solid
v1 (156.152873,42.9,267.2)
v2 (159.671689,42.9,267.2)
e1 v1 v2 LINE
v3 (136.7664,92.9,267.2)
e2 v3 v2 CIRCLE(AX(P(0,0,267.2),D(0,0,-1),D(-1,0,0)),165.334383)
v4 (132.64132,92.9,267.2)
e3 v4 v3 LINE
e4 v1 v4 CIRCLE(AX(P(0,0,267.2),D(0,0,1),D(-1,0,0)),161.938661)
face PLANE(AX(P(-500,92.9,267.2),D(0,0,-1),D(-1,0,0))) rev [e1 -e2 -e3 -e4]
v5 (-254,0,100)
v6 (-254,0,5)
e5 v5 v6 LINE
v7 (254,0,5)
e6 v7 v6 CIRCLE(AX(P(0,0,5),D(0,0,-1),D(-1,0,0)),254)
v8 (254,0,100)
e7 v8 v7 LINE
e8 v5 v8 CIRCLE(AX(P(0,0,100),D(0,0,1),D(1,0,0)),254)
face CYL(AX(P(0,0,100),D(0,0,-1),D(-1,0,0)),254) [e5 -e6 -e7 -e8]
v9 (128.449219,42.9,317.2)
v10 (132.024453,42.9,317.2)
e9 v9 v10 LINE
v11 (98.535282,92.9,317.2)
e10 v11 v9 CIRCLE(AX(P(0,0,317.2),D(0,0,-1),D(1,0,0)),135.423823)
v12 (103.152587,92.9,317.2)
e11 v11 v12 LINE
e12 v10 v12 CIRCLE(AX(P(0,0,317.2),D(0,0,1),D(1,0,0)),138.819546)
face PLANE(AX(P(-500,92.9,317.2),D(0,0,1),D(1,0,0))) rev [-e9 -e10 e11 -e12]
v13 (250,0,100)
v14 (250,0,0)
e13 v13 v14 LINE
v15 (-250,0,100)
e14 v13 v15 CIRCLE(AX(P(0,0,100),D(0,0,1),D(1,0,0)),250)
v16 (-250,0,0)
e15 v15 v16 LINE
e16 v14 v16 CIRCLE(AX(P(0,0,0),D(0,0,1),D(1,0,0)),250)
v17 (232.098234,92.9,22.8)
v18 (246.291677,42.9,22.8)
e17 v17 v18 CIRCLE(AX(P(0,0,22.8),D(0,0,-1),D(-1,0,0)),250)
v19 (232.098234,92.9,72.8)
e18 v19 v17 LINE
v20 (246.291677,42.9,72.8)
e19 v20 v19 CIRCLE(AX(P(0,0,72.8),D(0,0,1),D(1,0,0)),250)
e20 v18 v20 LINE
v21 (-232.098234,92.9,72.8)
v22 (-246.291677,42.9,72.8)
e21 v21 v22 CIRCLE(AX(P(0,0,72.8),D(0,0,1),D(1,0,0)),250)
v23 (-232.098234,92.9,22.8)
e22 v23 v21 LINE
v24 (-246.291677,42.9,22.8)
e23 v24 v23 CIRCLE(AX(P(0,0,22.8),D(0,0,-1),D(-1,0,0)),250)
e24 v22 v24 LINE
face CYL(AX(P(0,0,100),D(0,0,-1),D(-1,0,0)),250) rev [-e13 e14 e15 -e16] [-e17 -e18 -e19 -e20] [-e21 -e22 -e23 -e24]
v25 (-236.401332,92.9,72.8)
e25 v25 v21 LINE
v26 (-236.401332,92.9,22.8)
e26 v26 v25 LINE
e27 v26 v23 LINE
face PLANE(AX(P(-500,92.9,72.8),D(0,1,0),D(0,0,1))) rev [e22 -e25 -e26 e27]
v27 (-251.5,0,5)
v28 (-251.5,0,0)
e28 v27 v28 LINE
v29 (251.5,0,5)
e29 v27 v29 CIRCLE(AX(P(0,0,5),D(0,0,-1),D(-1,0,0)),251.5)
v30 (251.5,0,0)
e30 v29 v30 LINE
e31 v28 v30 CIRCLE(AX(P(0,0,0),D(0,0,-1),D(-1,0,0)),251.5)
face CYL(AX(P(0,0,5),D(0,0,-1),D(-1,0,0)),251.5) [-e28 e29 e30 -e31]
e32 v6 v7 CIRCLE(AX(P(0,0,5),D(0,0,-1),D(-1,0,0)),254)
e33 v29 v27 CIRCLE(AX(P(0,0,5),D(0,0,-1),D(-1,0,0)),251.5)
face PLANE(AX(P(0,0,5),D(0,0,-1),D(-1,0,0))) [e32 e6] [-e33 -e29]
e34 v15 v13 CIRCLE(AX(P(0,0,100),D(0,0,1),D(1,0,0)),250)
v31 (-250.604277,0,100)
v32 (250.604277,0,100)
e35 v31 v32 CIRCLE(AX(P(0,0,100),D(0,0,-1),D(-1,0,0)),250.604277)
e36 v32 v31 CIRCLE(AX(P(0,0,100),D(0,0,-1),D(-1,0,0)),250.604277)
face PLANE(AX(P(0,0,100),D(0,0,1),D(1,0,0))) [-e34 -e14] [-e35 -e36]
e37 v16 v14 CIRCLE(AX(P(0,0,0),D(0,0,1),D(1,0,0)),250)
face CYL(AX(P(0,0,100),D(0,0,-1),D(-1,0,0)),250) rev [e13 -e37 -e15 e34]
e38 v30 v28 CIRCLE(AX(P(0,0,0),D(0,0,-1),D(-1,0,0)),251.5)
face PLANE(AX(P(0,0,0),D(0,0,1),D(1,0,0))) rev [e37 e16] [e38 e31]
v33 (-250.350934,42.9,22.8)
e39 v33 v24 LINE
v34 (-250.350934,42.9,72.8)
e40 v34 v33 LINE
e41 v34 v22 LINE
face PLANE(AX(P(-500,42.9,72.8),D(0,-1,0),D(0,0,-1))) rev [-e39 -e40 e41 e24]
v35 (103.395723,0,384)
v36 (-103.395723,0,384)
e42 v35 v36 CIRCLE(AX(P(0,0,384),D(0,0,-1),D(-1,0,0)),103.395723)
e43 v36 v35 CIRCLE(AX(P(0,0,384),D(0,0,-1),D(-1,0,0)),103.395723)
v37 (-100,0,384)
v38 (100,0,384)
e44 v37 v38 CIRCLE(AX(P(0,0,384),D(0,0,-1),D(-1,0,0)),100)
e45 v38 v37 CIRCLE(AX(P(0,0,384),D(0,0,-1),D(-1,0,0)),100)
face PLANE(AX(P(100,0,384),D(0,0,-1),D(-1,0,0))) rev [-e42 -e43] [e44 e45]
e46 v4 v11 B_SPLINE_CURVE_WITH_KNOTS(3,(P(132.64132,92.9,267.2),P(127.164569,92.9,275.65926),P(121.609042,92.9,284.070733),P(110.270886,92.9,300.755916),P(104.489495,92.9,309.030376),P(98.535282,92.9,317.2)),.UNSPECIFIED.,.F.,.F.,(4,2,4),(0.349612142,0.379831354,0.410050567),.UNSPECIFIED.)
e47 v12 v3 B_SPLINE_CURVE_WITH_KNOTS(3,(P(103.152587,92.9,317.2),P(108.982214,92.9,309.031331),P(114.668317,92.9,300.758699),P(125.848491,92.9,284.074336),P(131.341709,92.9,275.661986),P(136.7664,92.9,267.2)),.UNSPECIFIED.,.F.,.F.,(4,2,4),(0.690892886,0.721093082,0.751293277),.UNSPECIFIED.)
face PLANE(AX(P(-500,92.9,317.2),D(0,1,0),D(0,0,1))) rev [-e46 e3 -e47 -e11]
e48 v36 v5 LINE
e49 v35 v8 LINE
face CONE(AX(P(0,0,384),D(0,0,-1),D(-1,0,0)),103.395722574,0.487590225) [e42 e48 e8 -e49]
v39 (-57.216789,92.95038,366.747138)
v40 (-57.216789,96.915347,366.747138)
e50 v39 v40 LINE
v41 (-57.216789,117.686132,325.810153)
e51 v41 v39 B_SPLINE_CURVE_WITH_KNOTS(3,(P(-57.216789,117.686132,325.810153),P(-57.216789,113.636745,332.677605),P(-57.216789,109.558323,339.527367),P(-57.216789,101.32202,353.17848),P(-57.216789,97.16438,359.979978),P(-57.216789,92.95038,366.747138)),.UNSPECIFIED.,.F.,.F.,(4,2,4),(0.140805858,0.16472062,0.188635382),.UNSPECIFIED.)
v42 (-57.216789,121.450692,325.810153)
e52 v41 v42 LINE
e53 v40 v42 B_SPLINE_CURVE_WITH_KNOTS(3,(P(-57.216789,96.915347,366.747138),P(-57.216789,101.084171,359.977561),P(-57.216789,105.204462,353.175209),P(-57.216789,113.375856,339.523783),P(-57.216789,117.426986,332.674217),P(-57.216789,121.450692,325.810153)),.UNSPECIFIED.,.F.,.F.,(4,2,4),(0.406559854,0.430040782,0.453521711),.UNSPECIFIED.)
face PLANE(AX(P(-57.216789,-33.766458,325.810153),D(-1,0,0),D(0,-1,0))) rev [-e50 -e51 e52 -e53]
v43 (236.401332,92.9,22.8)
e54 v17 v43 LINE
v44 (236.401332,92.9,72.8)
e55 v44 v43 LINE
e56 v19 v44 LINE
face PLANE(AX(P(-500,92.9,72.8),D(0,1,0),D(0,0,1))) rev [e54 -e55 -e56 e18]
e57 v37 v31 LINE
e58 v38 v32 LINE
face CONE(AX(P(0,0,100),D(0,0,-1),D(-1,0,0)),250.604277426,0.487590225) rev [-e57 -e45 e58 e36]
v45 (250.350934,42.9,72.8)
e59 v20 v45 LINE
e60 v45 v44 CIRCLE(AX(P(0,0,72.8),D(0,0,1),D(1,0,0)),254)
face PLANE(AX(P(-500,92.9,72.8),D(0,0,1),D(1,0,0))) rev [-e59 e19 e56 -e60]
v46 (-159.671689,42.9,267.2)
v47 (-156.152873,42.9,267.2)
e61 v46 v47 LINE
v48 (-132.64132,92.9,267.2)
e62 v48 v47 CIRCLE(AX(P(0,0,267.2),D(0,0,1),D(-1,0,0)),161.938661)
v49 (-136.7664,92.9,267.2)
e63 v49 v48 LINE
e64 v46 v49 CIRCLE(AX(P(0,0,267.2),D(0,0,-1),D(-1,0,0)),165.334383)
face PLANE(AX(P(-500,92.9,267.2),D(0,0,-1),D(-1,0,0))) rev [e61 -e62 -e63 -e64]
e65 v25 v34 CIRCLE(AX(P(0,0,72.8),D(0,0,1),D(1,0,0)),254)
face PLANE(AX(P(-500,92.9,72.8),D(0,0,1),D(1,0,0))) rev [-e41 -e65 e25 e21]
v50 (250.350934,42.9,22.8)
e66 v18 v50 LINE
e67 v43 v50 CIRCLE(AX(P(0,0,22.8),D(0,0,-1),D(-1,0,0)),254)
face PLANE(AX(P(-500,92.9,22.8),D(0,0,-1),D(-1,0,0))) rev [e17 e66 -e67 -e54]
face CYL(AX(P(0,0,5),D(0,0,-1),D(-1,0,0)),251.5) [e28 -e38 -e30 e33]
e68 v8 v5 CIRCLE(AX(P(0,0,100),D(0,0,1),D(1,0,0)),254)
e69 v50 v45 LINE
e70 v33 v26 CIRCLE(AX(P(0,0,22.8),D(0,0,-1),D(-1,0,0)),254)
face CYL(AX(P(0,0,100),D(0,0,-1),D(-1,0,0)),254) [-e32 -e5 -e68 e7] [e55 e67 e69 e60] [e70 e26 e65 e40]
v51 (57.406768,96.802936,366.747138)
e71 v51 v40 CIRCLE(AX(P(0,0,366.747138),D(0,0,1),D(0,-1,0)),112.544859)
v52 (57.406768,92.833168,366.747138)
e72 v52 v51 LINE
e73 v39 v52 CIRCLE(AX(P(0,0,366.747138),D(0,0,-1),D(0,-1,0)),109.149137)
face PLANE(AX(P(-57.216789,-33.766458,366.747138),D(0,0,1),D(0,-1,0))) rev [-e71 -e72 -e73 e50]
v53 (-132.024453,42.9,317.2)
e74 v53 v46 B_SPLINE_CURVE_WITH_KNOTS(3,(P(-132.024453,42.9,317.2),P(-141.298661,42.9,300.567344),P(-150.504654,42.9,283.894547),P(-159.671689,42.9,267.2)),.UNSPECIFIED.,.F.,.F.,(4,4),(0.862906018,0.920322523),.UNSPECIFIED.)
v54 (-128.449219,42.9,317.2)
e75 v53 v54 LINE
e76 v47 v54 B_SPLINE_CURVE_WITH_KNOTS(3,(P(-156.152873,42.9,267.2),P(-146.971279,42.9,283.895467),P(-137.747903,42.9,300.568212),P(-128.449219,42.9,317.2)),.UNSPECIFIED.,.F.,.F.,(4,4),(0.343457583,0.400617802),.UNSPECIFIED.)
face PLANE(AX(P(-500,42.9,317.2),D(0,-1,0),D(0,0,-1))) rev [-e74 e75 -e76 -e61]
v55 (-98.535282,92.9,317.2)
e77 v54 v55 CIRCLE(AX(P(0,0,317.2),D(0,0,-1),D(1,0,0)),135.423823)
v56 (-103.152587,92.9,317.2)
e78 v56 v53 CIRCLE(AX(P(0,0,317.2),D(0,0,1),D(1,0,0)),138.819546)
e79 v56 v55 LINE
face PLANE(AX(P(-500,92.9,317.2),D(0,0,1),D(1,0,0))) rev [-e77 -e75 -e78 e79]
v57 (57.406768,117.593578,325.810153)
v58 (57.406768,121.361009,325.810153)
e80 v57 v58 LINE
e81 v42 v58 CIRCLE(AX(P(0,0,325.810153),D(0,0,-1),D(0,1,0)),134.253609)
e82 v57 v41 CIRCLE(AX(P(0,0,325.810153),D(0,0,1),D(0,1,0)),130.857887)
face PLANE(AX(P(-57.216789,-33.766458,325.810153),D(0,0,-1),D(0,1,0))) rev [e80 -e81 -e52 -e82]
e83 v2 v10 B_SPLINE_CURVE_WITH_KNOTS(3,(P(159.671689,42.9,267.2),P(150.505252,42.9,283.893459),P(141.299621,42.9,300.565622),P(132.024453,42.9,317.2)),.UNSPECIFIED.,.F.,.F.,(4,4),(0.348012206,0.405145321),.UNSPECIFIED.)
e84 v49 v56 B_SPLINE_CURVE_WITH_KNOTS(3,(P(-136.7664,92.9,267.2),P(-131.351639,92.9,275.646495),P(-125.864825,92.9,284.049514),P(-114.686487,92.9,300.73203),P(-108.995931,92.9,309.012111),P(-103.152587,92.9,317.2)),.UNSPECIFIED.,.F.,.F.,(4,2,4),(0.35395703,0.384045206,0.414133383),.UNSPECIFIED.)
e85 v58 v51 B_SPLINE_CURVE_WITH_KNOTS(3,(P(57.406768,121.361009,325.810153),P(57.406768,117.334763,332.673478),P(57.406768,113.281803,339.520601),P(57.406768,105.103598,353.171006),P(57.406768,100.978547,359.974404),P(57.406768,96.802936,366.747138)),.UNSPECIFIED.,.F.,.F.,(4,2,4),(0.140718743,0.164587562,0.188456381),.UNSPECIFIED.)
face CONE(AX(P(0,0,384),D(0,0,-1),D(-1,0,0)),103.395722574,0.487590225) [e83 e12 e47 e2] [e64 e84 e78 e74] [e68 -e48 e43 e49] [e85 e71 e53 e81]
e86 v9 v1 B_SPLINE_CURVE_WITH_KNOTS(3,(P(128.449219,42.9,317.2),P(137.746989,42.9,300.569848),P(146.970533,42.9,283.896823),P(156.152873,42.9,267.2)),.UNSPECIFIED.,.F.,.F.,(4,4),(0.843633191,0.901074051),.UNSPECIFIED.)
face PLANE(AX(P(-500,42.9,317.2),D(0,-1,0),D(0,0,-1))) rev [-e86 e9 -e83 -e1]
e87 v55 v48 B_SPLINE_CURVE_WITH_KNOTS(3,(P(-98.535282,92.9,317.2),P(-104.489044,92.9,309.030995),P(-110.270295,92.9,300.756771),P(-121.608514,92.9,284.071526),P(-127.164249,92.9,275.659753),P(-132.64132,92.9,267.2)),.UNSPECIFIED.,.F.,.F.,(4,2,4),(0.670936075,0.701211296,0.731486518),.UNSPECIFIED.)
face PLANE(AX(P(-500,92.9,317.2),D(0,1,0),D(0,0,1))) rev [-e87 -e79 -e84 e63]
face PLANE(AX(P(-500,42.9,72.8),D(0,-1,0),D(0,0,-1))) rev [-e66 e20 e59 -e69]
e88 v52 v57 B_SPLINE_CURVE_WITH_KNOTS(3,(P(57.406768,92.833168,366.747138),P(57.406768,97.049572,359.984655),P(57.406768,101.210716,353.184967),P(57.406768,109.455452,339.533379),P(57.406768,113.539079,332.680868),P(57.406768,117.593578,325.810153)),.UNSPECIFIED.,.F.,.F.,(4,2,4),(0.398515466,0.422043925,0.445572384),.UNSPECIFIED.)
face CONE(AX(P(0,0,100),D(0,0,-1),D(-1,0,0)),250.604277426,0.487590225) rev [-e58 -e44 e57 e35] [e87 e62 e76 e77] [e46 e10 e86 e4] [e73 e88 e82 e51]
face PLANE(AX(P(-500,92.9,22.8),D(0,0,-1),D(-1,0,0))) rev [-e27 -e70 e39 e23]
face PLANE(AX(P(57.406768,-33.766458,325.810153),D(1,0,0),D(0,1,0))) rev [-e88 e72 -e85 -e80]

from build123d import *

# Parameters (mm, degrees)
SKETCH2_R           = 254
SKETCH2_R_2         = 250
BOSS_EXTRUDE1_DEPTH = 100
SKETCH7_W           = 50
SKETCH7_H           = 50
CUT_EXTRUDE3_DEPTH  = 500
SKETCH8_R           = 254
SKETCH8_R_2         = 251.5
CUT_EXTRUDE4_DEPTH  = 5
CUT_EXTRUDE5_START  = 100
SKETCH9_W           = 114.623557318
SKETCH9_H           = 40.936984757
CUT_EXTRUDE5_DEPTH  = 200


with BuildPart() as part:
    # Sketch2 → Boss-Extrude1 (new body)
    with BuildSketch(Plane.XY):
        Circle(SKETCH2_R)
        Circle(SKETCH2_R_2, mode=Mode.SUBTRACT)
    extrude(amount=BOSS_EXTRUDE1_DEPTH)

    # Sketch5 → Revolve1 (revolve)
    with BuildSketch(Plane(origin=(0, 0, 0), x_dir=(1, 0, 0), z_dir=(0, 1, 0)), mode=Mode.PRIVATE) as revolve1_sk:
        Polygon((254, -100), (103.395722574, -384), (100, -384), (250.604277426, -100), align=None)
    revolve(revolve1_sk.sketch.rotate(Axis((0, 0, 0), (0, 0, 1)), 180), axis=Axis((0, 0, 0), (0, 0, 1)))

    # Sketch7 → Cut-Extrude3 (cut, symmetric)
    with BuildSketch(Plane(origin=(0, 0, 0), x_dir=(0, 0, -1), z_dir=(1, 0, 0))):
        with Locations((-47.8, 67.9)):
            Rectangle(SKETCH7_W, SKETCH7_H)
        with Locations((-292.2, 67.9)):
            Rectangle(SKETCH7_W, SKETCH7_H)
    extrude(amount=CUT_EXTRUDE3_DEPTH, both=True, mode=Mode.SUBTRACT)

    # Sketch8 → Cut-Extrude4 (cut)
    with BuildSketch(Plane(origin=(0, 0, 0), x_dir=(-1, 0, 0), z_dir=(0, 0, -1))):
        Circle(SKETCH8_R)
        Circle(SKETCH8_R_2, mode=Mode.SUBTRACT)
    extrude(amount=-CUT_EXTRUDE4_DEPTH, mode=Mode.SUBTRACT)

    # Sketch9 → Cut-Extrude5 (cut)
    with BuildSketch(Plane(origin=(600, 66.233541641, 45.300312461), x_dir=(1, 0, 0), z_dir=(0, 1, 0)).offset(CUT_EXTRUDE5_START)):
        with Locations((-599.905010531, -300.978332918)):
            Rectangle(SKETCH9_W, SKETCH9_H)
    extrude(amount=-CUT_EXTRUDE5_DEPTH, mode=Mode.SUBTRACT)


solid = part.part
